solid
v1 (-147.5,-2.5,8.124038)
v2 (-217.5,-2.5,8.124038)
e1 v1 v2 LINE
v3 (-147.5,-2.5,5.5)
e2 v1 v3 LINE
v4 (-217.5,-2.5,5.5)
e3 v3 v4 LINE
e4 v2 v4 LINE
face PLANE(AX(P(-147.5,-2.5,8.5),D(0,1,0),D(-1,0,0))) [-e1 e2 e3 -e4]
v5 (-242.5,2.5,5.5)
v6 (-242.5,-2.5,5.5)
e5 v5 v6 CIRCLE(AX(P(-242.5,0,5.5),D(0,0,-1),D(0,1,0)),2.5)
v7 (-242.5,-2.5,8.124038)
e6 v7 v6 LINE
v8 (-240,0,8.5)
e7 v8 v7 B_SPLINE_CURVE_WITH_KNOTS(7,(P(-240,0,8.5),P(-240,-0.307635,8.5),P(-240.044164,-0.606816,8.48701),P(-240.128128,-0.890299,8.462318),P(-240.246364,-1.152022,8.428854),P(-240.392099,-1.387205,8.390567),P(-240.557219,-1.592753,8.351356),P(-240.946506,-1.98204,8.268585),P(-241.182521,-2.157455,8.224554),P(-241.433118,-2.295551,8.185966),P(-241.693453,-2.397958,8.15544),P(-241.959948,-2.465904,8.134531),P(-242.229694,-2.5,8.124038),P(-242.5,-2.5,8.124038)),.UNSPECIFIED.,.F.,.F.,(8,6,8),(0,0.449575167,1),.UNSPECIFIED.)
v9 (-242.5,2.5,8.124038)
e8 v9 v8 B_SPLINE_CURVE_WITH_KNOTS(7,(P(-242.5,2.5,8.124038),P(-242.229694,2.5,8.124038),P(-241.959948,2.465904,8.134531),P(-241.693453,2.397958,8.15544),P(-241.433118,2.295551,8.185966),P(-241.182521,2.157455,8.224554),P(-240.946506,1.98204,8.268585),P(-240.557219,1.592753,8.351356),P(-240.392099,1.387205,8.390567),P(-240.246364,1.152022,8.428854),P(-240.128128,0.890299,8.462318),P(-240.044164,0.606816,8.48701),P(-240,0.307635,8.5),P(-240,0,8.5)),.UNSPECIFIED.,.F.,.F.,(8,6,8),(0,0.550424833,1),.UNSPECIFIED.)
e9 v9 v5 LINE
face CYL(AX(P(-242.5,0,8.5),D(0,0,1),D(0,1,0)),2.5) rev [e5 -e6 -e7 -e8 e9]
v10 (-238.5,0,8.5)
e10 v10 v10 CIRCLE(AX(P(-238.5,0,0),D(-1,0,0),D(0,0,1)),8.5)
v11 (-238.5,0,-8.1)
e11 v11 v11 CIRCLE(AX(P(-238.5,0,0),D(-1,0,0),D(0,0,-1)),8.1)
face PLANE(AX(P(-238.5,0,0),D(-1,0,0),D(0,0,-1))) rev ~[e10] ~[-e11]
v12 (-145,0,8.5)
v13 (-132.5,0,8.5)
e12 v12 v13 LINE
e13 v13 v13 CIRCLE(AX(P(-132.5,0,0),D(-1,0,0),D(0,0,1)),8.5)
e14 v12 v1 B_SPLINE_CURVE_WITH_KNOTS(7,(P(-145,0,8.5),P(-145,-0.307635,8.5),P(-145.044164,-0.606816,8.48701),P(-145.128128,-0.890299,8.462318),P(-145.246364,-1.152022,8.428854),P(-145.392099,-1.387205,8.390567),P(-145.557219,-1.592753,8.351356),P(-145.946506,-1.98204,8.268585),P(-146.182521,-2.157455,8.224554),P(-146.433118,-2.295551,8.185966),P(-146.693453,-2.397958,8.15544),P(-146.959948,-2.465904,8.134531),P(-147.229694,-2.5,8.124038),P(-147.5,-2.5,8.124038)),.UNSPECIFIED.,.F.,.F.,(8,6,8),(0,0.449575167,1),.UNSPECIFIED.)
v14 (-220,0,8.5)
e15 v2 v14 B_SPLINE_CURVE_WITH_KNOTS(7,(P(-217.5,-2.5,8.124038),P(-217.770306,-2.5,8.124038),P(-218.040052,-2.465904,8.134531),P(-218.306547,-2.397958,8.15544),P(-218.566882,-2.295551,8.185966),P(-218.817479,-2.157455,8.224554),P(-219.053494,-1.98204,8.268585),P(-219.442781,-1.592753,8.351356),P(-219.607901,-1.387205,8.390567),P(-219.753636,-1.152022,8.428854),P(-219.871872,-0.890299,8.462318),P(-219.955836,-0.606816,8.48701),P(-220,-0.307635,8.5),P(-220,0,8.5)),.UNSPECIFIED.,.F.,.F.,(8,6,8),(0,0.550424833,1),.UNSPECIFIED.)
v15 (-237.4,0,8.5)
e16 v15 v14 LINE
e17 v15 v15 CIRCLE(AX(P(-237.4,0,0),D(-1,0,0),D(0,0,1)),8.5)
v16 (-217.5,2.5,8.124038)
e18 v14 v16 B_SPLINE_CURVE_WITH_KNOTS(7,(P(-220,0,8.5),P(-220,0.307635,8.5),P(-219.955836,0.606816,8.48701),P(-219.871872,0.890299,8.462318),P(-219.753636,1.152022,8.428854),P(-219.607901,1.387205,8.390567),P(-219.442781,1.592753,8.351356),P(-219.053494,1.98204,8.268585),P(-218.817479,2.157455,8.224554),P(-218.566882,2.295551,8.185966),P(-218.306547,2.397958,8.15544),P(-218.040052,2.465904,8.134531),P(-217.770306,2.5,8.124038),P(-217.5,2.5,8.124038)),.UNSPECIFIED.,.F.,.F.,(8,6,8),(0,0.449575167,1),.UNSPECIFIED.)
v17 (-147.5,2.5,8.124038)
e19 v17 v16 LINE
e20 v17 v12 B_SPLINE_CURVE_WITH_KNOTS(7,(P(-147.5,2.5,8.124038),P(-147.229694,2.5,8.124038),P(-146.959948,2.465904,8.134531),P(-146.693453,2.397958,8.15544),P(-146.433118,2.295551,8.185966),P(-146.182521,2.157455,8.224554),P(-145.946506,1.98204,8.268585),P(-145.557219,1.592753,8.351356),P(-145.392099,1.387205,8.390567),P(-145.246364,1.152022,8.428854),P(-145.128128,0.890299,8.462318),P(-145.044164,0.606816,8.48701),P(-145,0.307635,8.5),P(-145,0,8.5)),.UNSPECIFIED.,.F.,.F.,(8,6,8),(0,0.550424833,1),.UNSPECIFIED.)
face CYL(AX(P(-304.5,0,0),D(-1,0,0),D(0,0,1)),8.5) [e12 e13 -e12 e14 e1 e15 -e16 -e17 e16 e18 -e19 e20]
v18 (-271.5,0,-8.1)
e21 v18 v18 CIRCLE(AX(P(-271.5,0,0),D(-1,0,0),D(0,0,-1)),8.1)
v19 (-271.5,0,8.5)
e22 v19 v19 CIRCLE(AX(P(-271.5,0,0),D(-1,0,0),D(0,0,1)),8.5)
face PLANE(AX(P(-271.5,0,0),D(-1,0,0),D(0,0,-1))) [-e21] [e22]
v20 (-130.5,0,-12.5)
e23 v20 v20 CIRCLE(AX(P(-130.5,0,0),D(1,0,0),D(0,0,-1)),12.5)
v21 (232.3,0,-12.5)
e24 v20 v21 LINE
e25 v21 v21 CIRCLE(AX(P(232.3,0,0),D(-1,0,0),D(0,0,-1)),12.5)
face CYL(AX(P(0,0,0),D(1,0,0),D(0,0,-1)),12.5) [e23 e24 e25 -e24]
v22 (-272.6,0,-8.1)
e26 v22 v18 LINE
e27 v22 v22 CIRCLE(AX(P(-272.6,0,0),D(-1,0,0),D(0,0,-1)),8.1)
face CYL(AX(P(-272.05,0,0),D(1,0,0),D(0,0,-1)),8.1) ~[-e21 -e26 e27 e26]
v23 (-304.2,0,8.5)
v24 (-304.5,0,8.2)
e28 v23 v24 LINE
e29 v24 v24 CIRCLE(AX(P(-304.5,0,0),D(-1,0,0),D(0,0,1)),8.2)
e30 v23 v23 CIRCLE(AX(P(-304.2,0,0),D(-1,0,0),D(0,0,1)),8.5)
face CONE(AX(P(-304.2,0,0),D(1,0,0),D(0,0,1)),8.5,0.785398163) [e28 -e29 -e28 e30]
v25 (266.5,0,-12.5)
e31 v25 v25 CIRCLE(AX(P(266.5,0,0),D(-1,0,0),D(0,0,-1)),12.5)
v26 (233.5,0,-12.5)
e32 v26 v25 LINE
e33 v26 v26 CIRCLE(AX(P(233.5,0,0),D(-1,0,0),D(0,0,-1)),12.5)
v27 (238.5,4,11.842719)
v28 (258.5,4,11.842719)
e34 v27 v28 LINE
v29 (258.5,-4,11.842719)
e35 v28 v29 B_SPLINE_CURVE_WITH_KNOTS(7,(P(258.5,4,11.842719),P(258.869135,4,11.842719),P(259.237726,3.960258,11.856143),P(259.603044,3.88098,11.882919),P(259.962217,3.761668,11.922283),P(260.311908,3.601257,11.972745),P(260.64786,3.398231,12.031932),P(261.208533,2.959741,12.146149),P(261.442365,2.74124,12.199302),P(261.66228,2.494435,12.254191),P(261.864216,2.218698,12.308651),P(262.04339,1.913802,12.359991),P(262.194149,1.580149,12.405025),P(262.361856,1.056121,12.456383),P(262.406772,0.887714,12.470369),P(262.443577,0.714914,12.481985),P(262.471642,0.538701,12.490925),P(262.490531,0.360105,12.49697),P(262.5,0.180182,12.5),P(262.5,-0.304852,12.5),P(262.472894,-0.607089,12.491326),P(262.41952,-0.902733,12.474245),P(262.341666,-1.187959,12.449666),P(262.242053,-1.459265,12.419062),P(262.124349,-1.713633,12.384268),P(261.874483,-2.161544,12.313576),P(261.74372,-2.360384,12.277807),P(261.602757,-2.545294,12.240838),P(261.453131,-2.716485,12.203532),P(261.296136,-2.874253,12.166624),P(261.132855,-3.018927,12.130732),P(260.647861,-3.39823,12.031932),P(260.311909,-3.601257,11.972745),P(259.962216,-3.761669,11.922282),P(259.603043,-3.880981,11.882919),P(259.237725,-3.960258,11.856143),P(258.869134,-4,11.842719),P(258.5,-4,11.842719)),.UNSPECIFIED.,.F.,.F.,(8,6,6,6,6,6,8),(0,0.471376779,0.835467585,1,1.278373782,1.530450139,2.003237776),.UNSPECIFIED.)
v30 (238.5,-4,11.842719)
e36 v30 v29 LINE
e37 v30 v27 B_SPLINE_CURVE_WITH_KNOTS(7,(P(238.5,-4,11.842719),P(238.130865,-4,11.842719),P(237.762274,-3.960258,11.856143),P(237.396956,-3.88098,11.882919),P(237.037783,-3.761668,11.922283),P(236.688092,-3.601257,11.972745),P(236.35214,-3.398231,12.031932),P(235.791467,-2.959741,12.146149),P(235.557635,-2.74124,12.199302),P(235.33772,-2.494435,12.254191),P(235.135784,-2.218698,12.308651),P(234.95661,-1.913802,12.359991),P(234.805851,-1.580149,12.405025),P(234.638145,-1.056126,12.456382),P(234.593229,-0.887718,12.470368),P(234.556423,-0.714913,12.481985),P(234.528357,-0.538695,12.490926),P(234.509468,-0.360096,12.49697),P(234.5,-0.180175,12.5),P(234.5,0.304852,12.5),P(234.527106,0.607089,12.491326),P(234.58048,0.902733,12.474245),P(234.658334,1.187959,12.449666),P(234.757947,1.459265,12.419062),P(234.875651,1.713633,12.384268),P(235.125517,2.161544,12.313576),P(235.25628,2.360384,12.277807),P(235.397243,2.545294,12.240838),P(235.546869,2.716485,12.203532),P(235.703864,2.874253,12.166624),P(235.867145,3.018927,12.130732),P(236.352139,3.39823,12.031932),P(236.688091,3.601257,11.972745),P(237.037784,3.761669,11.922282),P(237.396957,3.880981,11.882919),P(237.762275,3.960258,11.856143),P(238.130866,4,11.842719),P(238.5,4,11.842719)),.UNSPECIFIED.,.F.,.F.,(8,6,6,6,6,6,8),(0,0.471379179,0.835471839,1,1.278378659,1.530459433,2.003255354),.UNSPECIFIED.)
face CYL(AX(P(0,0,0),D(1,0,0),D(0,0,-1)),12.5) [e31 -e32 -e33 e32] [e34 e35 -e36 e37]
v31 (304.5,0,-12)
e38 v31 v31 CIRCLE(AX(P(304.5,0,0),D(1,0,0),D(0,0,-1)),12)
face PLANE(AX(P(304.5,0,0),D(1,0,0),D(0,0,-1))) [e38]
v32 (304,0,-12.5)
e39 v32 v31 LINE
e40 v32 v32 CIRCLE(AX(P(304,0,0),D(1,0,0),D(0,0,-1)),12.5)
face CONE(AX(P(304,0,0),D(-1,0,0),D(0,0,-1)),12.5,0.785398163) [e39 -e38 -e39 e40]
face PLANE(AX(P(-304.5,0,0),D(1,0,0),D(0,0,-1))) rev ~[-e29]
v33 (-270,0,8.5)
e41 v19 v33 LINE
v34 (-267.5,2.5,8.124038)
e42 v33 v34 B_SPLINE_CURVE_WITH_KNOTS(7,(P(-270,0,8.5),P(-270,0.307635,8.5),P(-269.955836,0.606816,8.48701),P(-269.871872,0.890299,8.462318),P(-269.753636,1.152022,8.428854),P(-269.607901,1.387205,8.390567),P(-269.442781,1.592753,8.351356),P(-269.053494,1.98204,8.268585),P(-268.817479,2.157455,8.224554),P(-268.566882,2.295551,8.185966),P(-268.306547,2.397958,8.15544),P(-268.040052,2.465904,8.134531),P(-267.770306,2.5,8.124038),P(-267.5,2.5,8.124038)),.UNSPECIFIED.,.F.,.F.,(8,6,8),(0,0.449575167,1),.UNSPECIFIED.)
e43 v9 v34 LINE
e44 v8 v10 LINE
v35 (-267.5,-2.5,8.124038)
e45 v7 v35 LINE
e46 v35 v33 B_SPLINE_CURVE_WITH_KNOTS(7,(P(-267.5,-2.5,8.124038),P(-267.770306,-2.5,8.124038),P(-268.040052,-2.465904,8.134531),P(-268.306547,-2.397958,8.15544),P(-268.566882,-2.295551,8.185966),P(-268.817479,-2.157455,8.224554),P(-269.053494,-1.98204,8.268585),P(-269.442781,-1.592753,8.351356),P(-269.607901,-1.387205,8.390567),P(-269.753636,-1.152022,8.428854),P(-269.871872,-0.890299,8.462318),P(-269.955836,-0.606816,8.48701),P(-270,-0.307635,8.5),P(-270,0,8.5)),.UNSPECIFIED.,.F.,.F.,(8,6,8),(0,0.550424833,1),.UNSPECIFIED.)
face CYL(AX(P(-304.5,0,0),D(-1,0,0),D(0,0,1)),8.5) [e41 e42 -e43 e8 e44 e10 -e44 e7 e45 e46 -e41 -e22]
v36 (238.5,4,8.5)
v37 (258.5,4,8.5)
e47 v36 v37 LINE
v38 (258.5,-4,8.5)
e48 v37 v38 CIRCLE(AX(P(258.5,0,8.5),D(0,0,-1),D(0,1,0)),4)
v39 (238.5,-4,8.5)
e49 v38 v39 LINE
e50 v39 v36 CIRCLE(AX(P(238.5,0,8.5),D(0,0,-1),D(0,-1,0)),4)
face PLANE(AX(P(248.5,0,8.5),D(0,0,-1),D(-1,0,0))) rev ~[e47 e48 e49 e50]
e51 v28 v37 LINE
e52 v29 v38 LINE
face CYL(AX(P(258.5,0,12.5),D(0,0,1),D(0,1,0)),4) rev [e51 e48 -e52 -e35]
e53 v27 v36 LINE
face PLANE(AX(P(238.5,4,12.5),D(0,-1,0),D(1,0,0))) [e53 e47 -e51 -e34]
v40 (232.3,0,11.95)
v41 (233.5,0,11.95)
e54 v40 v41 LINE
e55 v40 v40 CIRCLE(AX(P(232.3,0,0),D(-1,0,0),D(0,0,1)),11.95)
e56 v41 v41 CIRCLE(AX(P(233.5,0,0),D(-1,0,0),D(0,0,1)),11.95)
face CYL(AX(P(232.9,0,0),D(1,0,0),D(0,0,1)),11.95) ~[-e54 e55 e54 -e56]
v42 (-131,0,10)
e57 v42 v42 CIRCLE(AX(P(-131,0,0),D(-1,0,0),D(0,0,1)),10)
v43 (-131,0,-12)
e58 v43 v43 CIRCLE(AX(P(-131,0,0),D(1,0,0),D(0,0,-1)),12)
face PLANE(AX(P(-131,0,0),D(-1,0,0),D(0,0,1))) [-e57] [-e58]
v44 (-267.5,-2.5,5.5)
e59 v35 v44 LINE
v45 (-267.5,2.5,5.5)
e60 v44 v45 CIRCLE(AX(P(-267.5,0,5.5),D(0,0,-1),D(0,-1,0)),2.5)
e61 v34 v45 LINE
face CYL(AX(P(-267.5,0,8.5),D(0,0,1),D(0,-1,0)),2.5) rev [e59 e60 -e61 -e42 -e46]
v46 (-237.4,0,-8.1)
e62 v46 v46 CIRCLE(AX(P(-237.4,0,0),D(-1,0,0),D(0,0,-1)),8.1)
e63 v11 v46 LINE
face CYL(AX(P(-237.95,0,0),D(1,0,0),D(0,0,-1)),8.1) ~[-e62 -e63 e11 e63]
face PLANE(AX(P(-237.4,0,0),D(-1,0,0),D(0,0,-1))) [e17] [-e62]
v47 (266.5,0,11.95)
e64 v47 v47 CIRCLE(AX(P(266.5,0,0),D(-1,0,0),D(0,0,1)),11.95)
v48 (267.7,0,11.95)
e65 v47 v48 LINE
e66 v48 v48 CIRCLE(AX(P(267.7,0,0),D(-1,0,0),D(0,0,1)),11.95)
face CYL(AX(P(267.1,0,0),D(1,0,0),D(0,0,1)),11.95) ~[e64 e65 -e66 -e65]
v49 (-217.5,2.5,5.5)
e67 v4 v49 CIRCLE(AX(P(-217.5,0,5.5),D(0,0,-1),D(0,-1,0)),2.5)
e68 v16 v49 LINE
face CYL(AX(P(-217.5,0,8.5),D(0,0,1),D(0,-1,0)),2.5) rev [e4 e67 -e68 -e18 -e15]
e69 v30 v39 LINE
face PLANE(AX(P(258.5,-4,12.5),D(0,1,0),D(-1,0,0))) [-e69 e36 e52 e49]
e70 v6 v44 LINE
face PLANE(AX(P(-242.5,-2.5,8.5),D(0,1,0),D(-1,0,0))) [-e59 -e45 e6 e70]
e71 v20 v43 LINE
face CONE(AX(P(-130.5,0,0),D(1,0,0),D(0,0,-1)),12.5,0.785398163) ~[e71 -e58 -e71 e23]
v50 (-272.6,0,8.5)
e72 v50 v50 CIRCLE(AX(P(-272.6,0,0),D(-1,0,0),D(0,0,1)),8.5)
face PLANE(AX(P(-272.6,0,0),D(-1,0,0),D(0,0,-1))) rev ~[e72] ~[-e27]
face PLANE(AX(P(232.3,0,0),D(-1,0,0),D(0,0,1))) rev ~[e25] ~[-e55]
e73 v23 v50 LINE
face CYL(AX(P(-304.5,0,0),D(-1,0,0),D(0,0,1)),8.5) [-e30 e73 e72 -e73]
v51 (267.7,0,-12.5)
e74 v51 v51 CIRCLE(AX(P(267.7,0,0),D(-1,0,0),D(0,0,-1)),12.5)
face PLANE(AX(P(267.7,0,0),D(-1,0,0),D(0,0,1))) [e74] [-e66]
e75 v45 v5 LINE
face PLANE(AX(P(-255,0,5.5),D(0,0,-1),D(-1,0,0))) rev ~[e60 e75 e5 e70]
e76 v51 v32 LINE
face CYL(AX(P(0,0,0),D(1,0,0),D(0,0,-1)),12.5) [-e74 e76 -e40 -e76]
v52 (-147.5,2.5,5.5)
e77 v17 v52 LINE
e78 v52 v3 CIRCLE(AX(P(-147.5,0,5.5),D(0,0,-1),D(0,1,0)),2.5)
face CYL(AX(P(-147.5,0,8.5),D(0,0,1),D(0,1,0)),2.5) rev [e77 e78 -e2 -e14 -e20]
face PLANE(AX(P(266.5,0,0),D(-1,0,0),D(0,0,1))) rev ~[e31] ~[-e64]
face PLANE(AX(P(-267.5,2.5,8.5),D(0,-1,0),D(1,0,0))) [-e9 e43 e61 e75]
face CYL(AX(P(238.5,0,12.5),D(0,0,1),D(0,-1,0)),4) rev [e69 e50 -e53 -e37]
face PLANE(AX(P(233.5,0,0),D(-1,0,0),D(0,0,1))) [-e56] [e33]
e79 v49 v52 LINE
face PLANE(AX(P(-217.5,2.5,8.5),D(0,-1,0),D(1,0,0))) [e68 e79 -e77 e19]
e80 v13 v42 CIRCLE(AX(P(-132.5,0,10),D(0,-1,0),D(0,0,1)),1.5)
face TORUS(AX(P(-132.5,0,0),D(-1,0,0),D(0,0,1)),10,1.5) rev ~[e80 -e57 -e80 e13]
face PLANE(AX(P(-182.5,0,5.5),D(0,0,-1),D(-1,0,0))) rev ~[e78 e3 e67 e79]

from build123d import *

# Parameters (mm, degrees)
SKETCH_2_R             = 12.5
EXTRUDE_1_DEPTH        = 304.5
SKETCH_3_OUTSIDE_W     = 149.006
SKETCH_3_OUTSIDE_H     = 149.006
SKETCH_3_OUTSIDE_R     = 8.5
CUT_EXTRUDE_1_DEPTH    = 173.5
CUT_EXTRUDE_2_DEPTH    = 3
CUT_EXTRUDE_3_DEPTH    = 4
CHAMFER_1_SIZE         = 0.5
CHAMFER_2_SIZE         = 0.3
SKETCH_8_W             = 1.2
SKETCH_8_H             = 0.55
PATTERN_LINEAR_2_COUNT = 2
PATTERN_LINEAR_2_PITCH = 34.2
SKETCH_9_W             = 1.1
SKETCH_9_H             = 0.4
PATTERN_LINEAR_3_COUNT = 2
PATTERN_LINEAR_3_PITCH = 34.1
FILLET_1_R             = 1.5


with BuildPart() as part:
    # 草图2 → 凸台-拉伸1 (new, symmetric)
    with BuildSketch(Plane(origin=(0, 0, 0), x_dir=(0, 0, -1), z_dir=(1, 0, 0))):
        Circle(SKETCH_2_R)
    extrude(amount=EXTRUDE_1_DEPTH, both=True)

    # 草图3 outside → 切除-拉伸1 (cut)
    with BuildSketch(Plane.ZY.offset(304.5)):
        Rectangle(SKETCH_3_OUTSIDE_W, SKETCH_3_OUTSIDE_H)
        Circle(SKETCH_3_OUTSIDE_R, mode=Mode.SUBTRACT)
    extrude(amount=-CUT_EXTRUDE_1_DEPTH, mode=Mode.SUBTRACT)

    # 草图5 → 切除-拉伸2 (cut)
    with BuildSketch(Plane.XY.offset(8.5)):
        with BuildLine():
            Line((-267.5, 2.5), (-242.5, 2.5))
            ThreePointArc((-242.5, 2.5), (-240, 0), (-242.5, -2.5))
            Line((-242.5, -2.5), (-267.5, -2.5))
            ThreePointArc((-267.5, -2.5), (-270, 0), (-267.5, 2.5))
        make_face()
        with BuildLine():
            Line((-217.5, 2.5), (-147.5, 2.5))
            ThreePointArc((-147.5, 2.5), (-145, 0), (-147.5, -2.5))
            Line((-147.5, -2.5), (-217.5, -2.5))
            ThreePointArc((-217.5, -2.5), (-220, 0), (-217.5, 2.5))
        make_face()
    extrude(amount=-CUT_EXTRUDE_2_DEPTH, mode=Mode.SUBTRACT)

    # 草图6 → 切除-拉伸3 (cut)
    with BuildSketch(Plane.XY.offset(12.5)):
        with BuildLine():
            Line((238.5, 4), (258.5, 4))
            ThreePointArc((258.5, 4), (262.5, 0), (258.5, -4))
            Line((258.5, -4), (238.5, -4))
            ThreePointArc((238.5, -4), (234.5, 0), (238.5, 4))
        make_face()
    extrude(amount=-CUT_EXTRUDE_3_DEPTH, mode=Mode.SUBTRACT)

    # 倒角1
    chamfer_1_edges = [part.edges().sort_by_distance(p)[0] for p in [
        (304.5, 0, 12.5),
        (-131, 0, 12.5),
    ]]
    chamfer(chamfer_1_edges, length=CHAMFER_1_SIZE)

    # 倒角2
    chamfer_2_edges = [part.edges().sort_by_distance(p)[0] for p in [
        (-304.5, 0, -8.5),
    ]]
    chamfer(chamfer_2_edges, length=CHAMFER_2_SIZE)

    # 草图8 → 切除-旋转2 (revolve, cut)
    with BuildSketch(Plane.XY, mode=Mode.PRIVATE) as cut_revolve_2_sk:
        with Locations((267.1, -12.225)):
            Rectangle(SKETCH_8_W, SKETCH_8_H)
    cut_revolve_2 = revolve(cut_revolve_2_sk.sketch.rotate(Axis((304.5, 0, 0), (-1, 0, 0)), 90), axis=Axis((304.5, 0, 0), (-1, 0, 0)), mode=Mode.SUBTRACT)

    # 阵列(线性)2: 切除-旋转2 ×2
    with Locations(*[(-i * PATTERN_LINEAR_2_PITCH, 0, 0) for i in range(1, PATTERN_LINEAR_2_COUNT)]):
        add(cut_revolve_2, mode=Mode.SUBTRACT)

    # 草图9 → 切除-旋转3 (revolve, cut)
    with BuildSketch(Plane.XY, mode=Mode.PRIVATE) as cut_revolve_3_sk:
        with Locations((-272.05, -8.3)):
            Rectangle(SKETCH_9_W, SKETCH_9_H)
    cut_revolve_3 = revolve(cut_revolve_3_sk.sketch.rotate(Axis((-131, 0, 0), (-1, 0, 0)), 270), axis=Axis((-131, 0, 0), (-1, 0, 0)), mode=Mode.SUBTRACT)

    # 阵列(线性)3: 切除-旋转3 ×2
    with Locations(*[(i * PATTERN_LINEAR_3_PITCH, 0, 0) for i in range(1, PATTERN_LINEAR_3_COUNT)]):
        add(cut_revolve_3, mode=Mode.SUBTRACT)

    # 圆角1
    fillet_1_edges = [part.edges().sort_by_distance(p)[0] for p in [
        (-131, 0, -8.5),
    ]]
    fillet(fillet_1_edges, radius=FILLET_1_R)


solid = part.part
